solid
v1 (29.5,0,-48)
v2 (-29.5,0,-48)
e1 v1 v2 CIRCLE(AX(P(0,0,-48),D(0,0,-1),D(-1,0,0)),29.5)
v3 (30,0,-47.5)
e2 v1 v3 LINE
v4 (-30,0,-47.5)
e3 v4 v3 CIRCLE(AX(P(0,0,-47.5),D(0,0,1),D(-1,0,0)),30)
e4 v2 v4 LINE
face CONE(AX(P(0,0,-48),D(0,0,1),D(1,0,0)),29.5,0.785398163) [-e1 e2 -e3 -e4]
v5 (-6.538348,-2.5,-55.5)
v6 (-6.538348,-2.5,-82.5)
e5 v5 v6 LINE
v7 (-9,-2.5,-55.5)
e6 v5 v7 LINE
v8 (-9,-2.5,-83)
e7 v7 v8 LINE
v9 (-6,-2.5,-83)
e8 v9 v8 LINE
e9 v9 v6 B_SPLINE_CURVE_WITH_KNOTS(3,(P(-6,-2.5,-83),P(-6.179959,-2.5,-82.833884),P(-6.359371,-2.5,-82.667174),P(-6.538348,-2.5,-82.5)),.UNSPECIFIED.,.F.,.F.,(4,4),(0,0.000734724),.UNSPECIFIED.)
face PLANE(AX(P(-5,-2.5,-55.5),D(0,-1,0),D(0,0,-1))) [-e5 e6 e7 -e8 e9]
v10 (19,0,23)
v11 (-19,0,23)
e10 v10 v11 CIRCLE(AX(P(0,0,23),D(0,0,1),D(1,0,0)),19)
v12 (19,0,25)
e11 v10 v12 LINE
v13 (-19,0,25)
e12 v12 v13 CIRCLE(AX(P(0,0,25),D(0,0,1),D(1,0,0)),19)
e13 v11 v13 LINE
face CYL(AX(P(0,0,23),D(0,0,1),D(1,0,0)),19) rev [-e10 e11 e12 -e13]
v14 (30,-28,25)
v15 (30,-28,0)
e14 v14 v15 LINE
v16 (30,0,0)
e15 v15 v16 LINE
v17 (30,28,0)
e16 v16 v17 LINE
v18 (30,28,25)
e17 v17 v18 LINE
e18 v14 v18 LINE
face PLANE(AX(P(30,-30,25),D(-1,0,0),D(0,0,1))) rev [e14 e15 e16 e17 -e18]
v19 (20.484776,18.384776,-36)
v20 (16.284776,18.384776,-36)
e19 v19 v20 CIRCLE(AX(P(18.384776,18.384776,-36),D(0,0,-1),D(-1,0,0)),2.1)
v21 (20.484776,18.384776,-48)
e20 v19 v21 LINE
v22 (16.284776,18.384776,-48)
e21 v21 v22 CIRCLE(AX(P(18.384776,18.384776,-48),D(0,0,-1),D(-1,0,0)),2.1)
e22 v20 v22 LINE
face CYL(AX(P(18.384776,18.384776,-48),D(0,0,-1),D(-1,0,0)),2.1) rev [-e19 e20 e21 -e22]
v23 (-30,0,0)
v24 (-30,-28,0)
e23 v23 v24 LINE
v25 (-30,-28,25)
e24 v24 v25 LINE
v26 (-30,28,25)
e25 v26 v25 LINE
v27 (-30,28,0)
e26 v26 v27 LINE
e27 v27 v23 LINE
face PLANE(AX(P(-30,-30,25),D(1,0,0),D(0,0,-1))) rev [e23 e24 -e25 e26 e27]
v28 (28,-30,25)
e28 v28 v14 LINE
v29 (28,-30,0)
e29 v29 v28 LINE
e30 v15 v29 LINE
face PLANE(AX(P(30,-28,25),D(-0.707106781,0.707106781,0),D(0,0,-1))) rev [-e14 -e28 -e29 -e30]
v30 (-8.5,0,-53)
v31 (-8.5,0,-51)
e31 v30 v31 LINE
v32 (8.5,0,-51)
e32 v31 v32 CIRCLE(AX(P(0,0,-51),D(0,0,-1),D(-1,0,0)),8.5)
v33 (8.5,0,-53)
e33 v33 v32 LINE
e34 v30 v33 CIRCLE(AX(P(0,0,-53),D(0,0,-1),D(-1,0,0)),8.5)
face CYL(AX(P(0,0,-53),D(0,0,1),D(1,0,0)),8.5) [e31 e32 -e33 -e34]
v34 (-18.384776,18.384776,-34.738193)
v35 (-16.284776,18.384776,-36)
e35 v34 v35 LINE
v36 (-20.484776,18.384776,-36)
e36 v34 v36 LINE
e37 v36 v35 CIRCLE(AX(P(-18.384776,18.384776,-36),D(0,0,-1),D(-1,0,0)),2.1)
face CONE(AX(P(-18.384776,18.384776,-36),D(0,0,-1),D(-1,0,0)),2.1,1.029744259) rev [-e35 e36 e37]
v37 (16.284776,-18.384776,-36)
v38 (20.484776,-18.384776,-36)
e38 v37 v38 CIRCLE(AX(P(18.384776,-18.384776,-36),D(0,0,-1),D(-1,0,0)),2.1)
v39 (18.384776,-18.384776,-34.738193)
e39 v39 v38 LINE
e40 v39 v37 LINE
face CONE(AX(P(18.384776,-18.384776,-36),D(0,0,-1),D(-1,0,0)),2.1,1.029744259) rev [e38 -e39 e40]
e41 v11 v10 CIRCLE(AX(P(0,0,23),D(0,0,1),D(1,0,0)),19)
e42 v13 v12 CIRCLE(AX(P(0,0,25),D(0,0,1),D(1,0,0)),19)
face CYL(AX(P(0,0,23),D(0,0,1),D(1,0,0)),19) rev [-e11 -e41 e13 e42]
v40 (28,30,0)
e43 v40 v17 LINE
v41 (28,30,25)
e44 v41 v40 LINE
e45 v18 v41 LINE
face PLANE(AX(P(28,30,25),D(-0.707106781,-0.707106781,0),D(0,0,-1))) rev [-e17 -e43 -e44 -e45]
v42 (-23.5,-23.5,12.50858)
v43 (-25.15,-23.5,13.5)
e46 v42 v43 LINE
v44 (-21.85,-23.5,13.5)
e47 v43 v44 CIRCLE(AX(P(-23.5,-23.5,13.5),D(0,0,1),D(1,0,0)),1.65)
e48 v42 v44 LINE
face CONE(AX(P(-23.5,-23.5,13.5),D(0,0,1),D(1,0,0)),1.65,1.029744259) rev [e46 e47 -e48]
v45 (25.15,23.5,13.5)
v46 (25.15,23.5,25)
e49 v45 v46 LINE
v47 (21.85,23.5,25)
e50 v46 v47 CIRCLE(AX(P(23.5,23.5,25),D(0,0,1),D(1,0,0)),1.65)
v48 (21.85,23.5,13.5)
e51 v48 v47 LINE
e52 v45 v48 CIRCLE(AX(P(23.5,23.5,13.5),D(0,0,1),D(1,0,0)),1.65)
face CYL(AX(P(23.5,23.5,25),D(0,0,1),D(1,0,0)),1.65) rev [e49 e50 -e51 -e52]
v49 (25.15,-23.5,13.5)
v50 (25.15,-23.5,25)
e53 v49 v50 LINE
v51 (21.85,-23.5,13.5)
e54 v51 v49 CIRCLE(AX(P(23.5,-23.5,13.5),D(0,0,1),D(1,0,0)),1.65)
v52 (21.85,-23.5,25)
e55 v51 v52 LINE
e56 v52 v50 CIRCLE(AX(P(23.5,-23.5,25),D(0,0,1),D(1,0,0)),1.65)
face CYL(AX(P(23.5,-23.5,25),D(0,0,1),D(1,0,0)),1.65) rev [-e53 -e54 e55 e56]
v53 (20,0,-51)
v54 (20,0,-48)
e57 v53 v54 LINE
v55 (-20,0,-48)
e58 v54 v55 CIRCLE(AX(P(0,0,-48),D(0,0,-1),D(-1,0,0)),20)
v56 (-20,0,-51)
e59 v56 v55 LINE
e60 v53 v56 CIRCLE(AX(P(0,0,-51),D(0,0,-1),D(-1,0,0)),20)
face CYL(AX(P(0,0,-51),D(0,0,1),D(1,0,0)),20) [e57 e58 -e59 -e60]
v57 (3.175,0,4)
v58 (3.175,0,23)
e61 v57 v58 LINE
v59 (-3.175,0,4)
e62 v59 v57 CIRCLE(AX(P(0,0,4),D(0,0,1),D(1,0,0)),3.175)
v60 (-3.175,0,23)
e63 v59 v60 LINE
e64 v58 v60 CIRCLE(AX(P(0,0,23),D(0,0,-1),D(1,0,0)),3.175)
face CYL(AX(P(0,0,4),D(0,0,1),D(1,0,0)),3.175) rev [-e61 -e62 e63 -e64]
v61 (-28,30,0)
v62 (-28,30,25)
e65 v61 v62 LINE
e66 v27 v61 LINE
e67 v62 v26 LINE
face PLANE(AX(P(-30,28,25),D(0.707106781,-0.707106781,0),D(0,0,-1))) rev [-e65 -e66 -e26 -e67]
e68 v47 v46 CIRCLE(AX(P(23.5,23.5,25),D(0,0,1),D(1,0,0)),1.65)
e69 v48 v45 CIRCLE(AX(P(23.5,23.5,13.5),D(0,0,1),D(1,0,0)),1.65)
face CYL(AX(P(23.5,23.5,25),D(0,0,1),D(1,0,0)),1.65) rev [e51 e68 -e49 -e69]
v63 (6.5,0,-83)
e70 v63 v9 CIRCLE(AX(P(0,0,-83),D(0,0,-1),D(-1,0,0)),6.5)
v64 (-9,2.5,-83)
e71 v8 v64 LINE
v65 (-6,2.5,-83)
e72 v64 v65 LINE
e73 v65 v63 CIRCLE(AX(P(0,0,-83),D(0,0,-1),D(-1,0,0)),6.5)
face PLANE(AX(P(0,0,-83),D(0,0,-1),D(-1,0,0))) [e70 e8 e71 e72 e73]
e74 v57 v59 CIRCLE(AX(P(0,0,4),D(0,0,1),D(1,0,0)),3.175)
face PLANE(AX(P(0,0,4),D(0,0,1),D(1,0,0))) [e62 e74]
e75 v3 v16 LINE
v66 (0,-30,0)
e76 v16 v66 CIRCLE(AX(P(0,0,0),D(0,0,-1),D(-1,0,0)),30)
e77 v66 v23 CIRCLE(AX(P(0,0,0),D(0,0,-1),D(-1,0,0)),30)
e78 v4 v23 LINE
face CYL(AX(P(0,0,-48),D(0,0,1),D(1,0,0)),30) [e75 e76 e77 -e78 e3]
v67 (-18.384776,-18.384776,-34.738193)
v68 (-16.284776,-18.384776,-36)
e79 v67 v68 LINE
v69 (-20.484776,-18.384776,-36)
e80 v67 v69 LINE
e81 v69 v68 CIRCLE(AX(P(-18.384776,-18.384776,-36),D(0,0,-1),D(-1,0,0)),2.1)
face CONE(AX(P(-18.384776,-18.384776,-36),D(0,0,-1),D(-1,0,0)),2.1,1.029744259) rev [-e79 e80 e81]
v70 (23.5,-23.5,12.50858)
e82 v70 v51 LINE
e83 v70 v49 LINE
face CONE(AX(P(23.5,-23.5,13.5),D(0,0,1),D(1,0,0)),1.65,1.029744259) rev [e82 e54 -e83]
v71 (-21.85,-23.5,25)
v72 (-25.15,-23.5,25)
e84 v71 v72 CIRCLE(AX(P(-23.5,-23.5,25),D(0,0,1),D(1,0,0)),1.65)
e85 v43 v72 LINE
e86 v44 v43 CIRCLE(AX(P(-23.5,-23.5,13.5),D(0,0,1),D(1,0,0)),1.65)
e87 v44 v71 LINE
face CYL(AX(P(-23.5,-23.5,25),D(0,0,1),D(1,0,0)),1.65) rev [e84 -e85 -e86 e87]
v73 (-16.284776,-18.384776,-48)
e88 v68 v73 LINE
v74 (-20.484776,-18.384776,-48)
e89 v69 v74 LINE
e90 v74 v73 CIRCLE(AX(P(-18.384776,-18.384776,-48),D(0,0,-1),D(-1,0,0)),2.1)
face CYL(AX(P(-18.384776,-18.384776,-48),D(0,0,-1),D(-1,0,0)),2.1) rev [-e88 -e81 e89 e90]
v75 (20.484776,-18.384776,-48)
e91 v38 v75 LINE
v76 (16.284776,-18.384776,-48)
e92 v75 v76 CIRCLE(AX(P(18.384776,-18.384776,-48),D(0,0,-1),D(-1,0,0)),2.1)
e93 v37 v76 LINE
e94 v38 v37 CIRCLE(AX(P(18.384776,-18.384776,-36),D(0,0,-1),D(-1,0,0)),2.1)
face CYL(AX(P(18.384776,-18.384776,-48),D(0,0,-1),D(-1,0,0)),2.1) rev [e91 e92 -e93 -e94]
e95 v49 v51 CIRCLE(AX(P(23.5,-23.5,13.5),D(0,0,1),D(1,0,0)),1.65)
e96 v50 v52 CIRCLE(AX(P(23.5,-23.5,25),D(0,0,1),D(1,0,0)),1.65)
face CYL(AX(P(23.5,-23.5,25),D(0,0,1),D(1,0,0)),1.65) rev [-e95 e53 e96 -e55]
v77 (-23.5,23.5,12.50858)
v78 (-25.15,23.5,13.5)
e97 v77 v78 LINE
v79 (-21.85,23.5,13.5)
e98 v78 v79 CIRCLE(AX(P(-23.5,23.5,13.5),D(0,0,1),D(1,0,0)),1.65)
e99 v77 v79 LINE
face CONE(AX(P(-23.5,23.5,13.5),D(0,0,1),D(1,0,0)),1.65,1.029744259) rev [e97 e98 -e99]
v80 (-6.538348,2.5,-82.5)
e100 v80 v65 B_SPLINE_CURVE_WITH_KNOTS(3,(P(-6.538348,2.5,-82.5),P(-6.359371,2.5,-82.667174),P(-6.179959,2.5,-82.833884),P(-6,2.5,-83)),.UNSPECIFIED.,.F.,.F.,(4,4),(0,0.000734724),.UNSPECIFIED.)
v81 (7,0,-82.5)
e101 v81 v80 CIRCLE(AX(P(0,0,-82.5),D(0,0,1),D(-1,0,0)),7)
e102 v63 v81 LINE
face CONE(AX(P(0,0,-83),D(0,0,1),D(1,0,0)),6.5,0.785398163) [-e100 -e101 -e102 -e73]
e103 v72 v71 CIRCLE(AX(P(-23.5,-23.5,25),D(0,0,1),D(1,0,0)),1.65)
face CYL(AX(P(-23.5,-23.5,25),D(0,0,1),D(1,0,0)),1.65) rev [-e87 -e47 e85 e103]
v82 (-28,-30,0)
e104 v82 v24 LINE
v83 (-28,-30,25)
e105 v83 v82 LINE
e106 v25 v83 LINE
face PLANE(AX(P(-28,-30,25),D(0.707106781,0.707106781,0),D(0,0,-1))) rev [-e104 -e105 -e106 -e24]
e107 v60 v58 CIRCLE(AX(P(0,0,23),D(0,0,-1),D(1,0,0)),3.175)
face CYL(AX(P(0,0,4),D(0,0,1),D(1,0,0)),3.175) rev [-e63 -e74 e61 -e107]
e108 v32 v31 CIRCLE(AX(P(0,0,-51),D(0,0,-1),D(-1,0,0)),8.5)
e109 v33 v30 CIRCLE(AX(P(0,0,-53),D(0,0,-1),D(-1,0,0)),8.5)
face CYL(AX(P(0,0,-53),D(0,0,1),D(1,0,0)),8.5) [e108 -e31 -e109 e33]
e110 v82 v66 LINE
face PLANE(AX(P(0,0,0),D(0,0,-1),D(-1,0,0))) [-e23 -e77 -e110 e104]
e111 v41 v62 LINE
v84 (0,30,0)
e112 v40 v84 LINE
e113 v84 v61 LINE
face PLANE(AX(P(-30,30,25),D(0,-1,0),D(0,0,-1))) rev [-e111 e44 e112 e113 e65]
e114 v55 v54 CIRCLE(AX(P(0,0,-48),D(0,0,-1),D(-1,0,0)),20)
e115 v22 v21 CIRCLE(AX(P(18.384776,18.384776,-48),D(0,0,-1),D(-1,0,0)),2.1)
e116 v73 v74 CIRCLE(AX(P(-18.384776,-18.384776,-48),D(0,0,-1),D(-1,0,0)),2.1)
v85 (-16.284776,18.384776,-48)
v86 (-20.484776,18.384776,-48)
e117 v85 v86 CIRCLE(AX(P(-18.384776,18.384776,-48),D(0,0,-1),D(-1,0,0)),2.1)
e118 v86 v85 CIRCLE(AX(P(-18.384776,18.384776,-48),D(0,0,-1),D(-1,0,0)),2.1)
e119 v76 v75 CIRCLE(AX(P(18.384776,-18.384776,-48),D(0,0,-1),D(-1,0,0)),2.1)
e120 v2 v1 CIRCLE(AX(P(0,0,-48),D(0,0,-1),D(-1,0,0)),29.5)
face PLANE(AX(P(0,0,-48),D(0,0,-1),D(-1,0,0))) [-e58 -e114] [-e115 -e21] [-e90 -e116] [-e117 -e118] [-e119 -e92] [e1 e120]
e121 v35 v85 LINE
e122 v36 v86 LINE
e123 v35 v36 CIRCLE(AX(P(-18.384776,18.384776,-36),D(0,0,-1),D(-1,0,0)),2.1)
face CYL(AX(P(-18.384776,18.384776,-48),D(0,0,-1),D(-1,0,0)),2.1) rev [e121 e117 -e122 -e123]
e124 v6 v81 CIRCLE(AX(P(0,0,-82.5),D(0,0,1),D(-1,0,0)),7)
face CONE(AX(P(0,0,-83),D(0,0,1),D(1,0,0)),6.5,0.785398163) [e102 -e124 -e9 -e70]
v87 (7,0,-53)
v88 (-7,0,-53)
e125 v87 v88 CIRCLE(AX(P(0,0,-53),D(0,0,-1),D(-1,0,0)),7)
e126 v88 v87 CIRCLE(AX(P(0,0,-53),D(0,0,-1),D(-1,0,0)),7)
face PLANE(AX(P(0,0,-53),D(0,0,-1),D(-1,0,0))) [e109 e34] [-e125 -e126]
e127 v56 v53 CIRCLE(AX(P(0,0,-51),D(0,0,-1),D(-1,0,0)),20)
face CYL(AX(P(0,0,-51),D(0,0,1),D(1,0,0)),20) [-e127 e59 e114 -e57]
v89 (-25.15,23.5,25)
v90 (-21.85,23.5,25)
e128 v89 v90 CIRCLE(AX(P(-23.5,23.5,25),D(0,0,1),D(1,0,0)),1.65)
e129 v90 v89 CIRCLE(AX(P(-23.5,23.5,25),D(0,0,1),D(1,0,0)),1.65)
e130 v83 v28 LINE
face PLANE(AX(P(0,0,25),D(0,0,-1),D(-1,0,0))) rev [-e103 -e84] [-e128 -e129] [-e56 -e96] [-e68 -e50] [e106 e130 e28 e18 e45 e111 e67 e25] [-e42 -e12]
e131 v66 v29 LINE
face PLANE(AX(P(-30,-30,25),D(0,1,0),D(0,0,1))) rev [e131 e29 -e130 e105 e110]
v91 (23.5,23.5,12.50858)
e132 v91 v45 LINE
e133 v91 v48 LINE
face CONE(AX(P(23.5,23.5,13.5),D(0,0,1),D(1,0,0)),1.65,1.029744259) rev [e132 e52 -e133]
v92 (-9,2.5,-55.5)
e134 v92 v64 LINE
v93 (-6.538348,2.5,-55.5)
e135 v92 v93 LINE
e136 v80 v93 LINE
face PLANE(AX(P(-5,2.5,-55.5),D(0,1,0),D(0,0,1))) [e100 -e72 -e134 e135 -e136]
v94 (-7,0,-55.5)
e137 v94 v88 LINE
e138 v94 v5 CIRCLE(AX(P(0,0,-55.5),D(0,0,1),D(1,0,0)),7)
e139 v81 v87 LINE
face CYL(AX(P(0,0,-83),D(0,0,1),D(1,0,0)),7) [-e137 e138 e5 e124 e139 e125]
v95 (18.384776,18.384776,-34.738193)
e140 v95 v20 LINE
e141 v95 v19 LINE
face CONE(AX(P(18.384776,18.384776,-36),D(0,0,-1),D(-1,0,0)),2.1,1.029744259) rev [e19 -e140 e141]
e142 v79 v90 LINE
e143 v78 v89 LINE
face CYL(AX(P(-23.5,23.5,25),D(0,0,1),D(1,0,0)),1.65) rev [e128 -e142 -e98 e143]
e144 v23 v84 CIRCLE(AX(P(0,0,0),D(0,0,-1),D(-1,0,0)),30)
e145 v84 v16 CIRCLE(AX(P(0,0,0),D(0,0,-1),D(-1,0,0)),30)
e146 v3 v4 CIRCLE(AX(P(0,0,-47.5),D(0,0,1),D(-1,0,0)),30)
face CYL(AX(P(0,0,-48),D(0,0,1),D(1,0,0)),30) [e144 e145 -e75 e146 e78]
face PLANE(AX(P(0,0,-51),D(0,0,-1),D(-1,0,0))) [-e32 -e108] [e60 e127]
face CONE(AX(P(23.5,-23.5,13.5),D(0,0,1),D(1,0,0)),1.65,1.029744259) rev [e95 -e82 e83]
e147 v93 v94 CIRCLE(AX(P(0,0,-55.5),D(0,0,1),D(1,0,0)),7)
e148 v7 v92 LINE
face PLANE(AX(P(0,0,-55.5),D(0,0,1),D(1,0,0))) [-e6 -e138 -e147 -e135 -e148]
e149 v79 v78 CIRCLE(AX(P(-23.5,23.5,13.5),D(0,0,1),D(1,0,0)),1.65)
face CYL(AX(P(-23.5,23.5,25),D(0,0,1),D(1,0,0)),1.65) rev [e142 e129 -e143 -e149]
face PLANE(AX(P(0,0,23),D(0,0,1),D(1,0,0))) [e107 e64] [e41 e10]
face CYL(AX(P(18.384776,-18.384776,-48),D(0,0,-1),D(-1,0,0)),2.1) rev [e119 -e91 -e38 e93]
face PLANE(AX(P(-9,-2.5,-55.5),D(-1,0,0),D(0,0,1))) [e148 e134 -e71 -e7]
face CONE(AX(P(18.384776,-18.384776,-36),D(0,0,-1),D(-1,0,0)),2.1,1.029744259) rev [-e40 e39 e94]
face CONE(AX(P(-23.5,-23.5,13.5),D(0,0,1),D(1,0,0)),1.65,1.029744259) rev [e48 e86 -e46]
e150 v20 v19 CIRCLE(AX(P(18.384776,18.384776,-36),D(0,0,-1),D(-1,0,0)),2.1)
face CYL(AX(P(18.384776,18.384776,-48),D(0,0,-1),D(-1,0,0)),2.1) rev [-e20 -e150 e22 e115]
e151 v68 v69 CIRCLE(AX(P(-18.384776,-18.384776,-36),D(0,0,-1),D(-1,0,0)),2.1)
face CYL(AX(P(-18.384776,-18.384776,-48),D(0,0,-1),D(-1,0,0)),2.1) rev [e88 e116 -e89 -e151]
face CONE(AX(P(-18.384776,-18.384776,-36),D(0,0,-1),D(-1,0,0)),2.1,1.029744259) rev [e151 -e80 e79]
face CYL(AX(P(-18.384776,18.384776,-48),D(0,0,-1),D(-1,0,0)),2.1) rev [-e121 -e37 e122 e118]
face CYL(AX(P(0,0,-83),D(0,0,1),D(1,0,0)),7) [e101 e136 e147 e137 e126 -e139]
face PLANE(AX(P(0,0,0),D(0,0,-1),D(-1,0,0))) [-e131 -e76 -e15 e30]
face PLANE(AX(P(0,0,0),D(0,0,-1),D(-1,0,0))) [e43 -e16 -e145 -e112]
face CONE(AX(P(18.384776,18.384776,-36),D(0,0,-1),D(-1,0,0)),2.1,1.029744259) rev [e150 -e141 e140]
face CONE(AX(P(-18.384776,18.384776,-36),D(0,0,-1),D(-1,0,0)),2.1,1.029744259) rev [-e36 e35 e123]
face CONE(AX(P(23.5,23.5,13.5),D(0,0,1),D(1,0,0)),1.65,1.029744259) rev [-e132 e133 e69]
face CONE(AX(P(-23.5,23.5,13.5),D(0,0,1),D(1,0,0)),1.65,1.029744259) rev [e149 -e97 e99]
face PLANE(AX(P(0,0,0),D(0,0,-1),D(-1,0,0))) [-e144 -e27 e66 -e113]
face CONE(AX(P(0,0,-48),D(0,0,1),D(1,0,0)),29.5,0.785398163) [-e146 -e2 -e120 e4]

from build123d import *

# Parameters (mm, degrees)
SKETCH_1_W               = 60
SKETCH_1_H               = 60
EXTRUDE_1_DEPTH          = 25
SKETCH_2_R               = 30
EXTRUDE_2_DEPTH          = 48
SKETCH_3_R               = 20
EXTRUDE_3_DEPTH          = 3
SKETCH_4_R               = 8.5
EXTRUDE_4_DEPTH          = 2
SKETCH_5_R               = 7
EXTRUDE_5_DEPTH          = 30
SKETCH_7_R               = 3.175
CUT_EXTRUDE_1_DEPTH      = 21
SKETCH_8_R               = 19
CUT_EXTRUDE_2_DEPTH      = 2
PATTERN_CIRCULAR_1_COUNT = 4
CHAMFER_1_SIZE           = 2
SKETCH_17_W              = 4
SKETCH_17_H              = 5
EXTRUDE_6_DEPTH          = 27.5
CHAMFER_2_SIZE           = 0.5


with BuildPart() as part:
    # 草图1 → 凸台-拉伸1 (new body)
    with BuildSketch(Plane.XY):
        Rectangle(SKETCH_1_W, SKETCH_1_H)
    extrude(amount=EXTRUDE_1_DEPTH)

    # 草图2 → 凸台-拉伸2 (add)
    with BuildSketch(Plane(origin=(0, 0, 0), x_dir=(-1, 0, 0), z_dir=(0, 0, -1))):
        Circle(SKETCH_2_R)
    extrude(amount=EXTRUDE_2_DEPTH)

    # 草图3 → 凸台-拉伸3 (add)
    with BuildSketch(Plane(origin=(0, 0, -48), x_dir=(-1, 0, 0), z_dir=(0, 0, -1))):
        Circle(SKETCH_3_R)
    extrude(amount=EXTRUDE_3_DEPTH)

    # 草图4 → 凸台-拉伸4 (add)
    with BuildSketch(Plane(origin=(0, 0, -51), x_dir=(-1, 0, 0), z_dir=(0, 0, -1))):
        Circle(SKETCH_4_R)
    extrude(amount=EXTRUDE_4_DEPTH)

    # 草图5 → 凸台-拉伸5 (add)
    with BuildSketch(Plane(origin=(0, 0, -53), x_dir=(-1, 0, 0), z_dir=(0, 0, -1))):
        Circle(SKETCH_5_R)
    extrude(amount=EXTRUDE_5_DEPTH)

    # 草图7 → 切除-拉伸1 (cut)
    with BuildSketch(Plane.XY.offset(25)):
        Circle(SKETCH_7_R)
    extrude(amount=-CUT_EXTRUDE_1_DEPTH, mode=Mode.SUBTRACT)

    # 草图8 → 切除-拉伸2 (cut)
    with BuildSketch(Plane.XY.offset(25)):
        Circle(SKETCH_8_R)
    extrude(amount=-CUT_EXTRUDE_2_DEPTH, mode=Mode.SUBTRACT)

    # 草图10 → M4 螺纹孔1 (revolve, cut)
    with BuildSketch(Plane(origin=(23.5, 23.5, 25), x_dir=(0, -1, 0), z_dir=(1, 0, 0))):
        Polygon((0, 0), (0, 12.491420021), (1.65, 11.5), (1.65, 0), align=None)
    hole_wizard_m4_1 = revolve(axis=Axis((23.5, 23.5, 31.35), (0, 0, -1)), mode=Mode.SUBTRACT)

    # 草图15 → M5 螺纹孔1 (revolve, cut)
    with BuildSketch(Plane(origin=(-18.384776311, 18.384776311, -48), x_dir=(0, 1, 0), z_dir=(1, 0, 0))):
        Polygon((0, 0), (0, 13.2618073), (2.1, 12), (2.1, 0), align=None)
    hole_wizard_m5_1 = revolve(axis=Axis((-18.384776311, 18.384776311, -54.35), (0, 0, 1)), mode=Mode.SUBTRACT)

    # 阵列(圆周)1: M4 螺纹孔1, M5 螺纹孔1 ×4 about axis
    pattern_circular_1_axis = Axis((0, 0, 0), (0, 0, 1))
    add([hole_wizard_m4_1.rotate(pattern_circular_1_axis, i * 360 / PATTERN_CIRCULAR_1_COUNT) for i in range(1, PATTERN_CIRCULAR_1_COUNT)], mode=Mode.SUBTRACT)
    add([hole_wizard_m5_1.rotate(pattern_circular_1_axis, i * 360 / PATTERN_CIRCULAR_1_COUNT) for i in range(1, PATTERN_CIRCULAR_1_COUNT)], mode=Mode.SUBTRACT)

    # 倒角1
    chamfer_1_edges = [part.edges().sort_by_distance(p)[0] for p in [
        (30, -30, 12.5),
        (-30, -30, 12.5),
        (-30, 30, 12.5),
        (30, 30, 12.5),
    ]]
    chamfer(chamfer_1_edges, length=CHAMFER_1_SIZE)

    # 草图17 → 凸台-拉伸6 (add)
    with BuildSketch(Plane(origin=(0, 0, -83), x_dir=(-1, 0, 0), z_dir=(0, 0, -1))):
        with Locations((7, 0)):
            Rectangle(SKETCH_17_W, SKETCH_17_H)
    extrude(amount=-EXTRUDE_6_DEPTH)

    # 倒角2
    chamfer_2_edges = [part.edges().sort_by_distance(p)[0] for p in [
        (30, 0, -48),
        (7, 0, -83),
    ]]
    chamfer(chamfer_2_edges, length=CHAMFER_2_SIZE)


solid = part.part
